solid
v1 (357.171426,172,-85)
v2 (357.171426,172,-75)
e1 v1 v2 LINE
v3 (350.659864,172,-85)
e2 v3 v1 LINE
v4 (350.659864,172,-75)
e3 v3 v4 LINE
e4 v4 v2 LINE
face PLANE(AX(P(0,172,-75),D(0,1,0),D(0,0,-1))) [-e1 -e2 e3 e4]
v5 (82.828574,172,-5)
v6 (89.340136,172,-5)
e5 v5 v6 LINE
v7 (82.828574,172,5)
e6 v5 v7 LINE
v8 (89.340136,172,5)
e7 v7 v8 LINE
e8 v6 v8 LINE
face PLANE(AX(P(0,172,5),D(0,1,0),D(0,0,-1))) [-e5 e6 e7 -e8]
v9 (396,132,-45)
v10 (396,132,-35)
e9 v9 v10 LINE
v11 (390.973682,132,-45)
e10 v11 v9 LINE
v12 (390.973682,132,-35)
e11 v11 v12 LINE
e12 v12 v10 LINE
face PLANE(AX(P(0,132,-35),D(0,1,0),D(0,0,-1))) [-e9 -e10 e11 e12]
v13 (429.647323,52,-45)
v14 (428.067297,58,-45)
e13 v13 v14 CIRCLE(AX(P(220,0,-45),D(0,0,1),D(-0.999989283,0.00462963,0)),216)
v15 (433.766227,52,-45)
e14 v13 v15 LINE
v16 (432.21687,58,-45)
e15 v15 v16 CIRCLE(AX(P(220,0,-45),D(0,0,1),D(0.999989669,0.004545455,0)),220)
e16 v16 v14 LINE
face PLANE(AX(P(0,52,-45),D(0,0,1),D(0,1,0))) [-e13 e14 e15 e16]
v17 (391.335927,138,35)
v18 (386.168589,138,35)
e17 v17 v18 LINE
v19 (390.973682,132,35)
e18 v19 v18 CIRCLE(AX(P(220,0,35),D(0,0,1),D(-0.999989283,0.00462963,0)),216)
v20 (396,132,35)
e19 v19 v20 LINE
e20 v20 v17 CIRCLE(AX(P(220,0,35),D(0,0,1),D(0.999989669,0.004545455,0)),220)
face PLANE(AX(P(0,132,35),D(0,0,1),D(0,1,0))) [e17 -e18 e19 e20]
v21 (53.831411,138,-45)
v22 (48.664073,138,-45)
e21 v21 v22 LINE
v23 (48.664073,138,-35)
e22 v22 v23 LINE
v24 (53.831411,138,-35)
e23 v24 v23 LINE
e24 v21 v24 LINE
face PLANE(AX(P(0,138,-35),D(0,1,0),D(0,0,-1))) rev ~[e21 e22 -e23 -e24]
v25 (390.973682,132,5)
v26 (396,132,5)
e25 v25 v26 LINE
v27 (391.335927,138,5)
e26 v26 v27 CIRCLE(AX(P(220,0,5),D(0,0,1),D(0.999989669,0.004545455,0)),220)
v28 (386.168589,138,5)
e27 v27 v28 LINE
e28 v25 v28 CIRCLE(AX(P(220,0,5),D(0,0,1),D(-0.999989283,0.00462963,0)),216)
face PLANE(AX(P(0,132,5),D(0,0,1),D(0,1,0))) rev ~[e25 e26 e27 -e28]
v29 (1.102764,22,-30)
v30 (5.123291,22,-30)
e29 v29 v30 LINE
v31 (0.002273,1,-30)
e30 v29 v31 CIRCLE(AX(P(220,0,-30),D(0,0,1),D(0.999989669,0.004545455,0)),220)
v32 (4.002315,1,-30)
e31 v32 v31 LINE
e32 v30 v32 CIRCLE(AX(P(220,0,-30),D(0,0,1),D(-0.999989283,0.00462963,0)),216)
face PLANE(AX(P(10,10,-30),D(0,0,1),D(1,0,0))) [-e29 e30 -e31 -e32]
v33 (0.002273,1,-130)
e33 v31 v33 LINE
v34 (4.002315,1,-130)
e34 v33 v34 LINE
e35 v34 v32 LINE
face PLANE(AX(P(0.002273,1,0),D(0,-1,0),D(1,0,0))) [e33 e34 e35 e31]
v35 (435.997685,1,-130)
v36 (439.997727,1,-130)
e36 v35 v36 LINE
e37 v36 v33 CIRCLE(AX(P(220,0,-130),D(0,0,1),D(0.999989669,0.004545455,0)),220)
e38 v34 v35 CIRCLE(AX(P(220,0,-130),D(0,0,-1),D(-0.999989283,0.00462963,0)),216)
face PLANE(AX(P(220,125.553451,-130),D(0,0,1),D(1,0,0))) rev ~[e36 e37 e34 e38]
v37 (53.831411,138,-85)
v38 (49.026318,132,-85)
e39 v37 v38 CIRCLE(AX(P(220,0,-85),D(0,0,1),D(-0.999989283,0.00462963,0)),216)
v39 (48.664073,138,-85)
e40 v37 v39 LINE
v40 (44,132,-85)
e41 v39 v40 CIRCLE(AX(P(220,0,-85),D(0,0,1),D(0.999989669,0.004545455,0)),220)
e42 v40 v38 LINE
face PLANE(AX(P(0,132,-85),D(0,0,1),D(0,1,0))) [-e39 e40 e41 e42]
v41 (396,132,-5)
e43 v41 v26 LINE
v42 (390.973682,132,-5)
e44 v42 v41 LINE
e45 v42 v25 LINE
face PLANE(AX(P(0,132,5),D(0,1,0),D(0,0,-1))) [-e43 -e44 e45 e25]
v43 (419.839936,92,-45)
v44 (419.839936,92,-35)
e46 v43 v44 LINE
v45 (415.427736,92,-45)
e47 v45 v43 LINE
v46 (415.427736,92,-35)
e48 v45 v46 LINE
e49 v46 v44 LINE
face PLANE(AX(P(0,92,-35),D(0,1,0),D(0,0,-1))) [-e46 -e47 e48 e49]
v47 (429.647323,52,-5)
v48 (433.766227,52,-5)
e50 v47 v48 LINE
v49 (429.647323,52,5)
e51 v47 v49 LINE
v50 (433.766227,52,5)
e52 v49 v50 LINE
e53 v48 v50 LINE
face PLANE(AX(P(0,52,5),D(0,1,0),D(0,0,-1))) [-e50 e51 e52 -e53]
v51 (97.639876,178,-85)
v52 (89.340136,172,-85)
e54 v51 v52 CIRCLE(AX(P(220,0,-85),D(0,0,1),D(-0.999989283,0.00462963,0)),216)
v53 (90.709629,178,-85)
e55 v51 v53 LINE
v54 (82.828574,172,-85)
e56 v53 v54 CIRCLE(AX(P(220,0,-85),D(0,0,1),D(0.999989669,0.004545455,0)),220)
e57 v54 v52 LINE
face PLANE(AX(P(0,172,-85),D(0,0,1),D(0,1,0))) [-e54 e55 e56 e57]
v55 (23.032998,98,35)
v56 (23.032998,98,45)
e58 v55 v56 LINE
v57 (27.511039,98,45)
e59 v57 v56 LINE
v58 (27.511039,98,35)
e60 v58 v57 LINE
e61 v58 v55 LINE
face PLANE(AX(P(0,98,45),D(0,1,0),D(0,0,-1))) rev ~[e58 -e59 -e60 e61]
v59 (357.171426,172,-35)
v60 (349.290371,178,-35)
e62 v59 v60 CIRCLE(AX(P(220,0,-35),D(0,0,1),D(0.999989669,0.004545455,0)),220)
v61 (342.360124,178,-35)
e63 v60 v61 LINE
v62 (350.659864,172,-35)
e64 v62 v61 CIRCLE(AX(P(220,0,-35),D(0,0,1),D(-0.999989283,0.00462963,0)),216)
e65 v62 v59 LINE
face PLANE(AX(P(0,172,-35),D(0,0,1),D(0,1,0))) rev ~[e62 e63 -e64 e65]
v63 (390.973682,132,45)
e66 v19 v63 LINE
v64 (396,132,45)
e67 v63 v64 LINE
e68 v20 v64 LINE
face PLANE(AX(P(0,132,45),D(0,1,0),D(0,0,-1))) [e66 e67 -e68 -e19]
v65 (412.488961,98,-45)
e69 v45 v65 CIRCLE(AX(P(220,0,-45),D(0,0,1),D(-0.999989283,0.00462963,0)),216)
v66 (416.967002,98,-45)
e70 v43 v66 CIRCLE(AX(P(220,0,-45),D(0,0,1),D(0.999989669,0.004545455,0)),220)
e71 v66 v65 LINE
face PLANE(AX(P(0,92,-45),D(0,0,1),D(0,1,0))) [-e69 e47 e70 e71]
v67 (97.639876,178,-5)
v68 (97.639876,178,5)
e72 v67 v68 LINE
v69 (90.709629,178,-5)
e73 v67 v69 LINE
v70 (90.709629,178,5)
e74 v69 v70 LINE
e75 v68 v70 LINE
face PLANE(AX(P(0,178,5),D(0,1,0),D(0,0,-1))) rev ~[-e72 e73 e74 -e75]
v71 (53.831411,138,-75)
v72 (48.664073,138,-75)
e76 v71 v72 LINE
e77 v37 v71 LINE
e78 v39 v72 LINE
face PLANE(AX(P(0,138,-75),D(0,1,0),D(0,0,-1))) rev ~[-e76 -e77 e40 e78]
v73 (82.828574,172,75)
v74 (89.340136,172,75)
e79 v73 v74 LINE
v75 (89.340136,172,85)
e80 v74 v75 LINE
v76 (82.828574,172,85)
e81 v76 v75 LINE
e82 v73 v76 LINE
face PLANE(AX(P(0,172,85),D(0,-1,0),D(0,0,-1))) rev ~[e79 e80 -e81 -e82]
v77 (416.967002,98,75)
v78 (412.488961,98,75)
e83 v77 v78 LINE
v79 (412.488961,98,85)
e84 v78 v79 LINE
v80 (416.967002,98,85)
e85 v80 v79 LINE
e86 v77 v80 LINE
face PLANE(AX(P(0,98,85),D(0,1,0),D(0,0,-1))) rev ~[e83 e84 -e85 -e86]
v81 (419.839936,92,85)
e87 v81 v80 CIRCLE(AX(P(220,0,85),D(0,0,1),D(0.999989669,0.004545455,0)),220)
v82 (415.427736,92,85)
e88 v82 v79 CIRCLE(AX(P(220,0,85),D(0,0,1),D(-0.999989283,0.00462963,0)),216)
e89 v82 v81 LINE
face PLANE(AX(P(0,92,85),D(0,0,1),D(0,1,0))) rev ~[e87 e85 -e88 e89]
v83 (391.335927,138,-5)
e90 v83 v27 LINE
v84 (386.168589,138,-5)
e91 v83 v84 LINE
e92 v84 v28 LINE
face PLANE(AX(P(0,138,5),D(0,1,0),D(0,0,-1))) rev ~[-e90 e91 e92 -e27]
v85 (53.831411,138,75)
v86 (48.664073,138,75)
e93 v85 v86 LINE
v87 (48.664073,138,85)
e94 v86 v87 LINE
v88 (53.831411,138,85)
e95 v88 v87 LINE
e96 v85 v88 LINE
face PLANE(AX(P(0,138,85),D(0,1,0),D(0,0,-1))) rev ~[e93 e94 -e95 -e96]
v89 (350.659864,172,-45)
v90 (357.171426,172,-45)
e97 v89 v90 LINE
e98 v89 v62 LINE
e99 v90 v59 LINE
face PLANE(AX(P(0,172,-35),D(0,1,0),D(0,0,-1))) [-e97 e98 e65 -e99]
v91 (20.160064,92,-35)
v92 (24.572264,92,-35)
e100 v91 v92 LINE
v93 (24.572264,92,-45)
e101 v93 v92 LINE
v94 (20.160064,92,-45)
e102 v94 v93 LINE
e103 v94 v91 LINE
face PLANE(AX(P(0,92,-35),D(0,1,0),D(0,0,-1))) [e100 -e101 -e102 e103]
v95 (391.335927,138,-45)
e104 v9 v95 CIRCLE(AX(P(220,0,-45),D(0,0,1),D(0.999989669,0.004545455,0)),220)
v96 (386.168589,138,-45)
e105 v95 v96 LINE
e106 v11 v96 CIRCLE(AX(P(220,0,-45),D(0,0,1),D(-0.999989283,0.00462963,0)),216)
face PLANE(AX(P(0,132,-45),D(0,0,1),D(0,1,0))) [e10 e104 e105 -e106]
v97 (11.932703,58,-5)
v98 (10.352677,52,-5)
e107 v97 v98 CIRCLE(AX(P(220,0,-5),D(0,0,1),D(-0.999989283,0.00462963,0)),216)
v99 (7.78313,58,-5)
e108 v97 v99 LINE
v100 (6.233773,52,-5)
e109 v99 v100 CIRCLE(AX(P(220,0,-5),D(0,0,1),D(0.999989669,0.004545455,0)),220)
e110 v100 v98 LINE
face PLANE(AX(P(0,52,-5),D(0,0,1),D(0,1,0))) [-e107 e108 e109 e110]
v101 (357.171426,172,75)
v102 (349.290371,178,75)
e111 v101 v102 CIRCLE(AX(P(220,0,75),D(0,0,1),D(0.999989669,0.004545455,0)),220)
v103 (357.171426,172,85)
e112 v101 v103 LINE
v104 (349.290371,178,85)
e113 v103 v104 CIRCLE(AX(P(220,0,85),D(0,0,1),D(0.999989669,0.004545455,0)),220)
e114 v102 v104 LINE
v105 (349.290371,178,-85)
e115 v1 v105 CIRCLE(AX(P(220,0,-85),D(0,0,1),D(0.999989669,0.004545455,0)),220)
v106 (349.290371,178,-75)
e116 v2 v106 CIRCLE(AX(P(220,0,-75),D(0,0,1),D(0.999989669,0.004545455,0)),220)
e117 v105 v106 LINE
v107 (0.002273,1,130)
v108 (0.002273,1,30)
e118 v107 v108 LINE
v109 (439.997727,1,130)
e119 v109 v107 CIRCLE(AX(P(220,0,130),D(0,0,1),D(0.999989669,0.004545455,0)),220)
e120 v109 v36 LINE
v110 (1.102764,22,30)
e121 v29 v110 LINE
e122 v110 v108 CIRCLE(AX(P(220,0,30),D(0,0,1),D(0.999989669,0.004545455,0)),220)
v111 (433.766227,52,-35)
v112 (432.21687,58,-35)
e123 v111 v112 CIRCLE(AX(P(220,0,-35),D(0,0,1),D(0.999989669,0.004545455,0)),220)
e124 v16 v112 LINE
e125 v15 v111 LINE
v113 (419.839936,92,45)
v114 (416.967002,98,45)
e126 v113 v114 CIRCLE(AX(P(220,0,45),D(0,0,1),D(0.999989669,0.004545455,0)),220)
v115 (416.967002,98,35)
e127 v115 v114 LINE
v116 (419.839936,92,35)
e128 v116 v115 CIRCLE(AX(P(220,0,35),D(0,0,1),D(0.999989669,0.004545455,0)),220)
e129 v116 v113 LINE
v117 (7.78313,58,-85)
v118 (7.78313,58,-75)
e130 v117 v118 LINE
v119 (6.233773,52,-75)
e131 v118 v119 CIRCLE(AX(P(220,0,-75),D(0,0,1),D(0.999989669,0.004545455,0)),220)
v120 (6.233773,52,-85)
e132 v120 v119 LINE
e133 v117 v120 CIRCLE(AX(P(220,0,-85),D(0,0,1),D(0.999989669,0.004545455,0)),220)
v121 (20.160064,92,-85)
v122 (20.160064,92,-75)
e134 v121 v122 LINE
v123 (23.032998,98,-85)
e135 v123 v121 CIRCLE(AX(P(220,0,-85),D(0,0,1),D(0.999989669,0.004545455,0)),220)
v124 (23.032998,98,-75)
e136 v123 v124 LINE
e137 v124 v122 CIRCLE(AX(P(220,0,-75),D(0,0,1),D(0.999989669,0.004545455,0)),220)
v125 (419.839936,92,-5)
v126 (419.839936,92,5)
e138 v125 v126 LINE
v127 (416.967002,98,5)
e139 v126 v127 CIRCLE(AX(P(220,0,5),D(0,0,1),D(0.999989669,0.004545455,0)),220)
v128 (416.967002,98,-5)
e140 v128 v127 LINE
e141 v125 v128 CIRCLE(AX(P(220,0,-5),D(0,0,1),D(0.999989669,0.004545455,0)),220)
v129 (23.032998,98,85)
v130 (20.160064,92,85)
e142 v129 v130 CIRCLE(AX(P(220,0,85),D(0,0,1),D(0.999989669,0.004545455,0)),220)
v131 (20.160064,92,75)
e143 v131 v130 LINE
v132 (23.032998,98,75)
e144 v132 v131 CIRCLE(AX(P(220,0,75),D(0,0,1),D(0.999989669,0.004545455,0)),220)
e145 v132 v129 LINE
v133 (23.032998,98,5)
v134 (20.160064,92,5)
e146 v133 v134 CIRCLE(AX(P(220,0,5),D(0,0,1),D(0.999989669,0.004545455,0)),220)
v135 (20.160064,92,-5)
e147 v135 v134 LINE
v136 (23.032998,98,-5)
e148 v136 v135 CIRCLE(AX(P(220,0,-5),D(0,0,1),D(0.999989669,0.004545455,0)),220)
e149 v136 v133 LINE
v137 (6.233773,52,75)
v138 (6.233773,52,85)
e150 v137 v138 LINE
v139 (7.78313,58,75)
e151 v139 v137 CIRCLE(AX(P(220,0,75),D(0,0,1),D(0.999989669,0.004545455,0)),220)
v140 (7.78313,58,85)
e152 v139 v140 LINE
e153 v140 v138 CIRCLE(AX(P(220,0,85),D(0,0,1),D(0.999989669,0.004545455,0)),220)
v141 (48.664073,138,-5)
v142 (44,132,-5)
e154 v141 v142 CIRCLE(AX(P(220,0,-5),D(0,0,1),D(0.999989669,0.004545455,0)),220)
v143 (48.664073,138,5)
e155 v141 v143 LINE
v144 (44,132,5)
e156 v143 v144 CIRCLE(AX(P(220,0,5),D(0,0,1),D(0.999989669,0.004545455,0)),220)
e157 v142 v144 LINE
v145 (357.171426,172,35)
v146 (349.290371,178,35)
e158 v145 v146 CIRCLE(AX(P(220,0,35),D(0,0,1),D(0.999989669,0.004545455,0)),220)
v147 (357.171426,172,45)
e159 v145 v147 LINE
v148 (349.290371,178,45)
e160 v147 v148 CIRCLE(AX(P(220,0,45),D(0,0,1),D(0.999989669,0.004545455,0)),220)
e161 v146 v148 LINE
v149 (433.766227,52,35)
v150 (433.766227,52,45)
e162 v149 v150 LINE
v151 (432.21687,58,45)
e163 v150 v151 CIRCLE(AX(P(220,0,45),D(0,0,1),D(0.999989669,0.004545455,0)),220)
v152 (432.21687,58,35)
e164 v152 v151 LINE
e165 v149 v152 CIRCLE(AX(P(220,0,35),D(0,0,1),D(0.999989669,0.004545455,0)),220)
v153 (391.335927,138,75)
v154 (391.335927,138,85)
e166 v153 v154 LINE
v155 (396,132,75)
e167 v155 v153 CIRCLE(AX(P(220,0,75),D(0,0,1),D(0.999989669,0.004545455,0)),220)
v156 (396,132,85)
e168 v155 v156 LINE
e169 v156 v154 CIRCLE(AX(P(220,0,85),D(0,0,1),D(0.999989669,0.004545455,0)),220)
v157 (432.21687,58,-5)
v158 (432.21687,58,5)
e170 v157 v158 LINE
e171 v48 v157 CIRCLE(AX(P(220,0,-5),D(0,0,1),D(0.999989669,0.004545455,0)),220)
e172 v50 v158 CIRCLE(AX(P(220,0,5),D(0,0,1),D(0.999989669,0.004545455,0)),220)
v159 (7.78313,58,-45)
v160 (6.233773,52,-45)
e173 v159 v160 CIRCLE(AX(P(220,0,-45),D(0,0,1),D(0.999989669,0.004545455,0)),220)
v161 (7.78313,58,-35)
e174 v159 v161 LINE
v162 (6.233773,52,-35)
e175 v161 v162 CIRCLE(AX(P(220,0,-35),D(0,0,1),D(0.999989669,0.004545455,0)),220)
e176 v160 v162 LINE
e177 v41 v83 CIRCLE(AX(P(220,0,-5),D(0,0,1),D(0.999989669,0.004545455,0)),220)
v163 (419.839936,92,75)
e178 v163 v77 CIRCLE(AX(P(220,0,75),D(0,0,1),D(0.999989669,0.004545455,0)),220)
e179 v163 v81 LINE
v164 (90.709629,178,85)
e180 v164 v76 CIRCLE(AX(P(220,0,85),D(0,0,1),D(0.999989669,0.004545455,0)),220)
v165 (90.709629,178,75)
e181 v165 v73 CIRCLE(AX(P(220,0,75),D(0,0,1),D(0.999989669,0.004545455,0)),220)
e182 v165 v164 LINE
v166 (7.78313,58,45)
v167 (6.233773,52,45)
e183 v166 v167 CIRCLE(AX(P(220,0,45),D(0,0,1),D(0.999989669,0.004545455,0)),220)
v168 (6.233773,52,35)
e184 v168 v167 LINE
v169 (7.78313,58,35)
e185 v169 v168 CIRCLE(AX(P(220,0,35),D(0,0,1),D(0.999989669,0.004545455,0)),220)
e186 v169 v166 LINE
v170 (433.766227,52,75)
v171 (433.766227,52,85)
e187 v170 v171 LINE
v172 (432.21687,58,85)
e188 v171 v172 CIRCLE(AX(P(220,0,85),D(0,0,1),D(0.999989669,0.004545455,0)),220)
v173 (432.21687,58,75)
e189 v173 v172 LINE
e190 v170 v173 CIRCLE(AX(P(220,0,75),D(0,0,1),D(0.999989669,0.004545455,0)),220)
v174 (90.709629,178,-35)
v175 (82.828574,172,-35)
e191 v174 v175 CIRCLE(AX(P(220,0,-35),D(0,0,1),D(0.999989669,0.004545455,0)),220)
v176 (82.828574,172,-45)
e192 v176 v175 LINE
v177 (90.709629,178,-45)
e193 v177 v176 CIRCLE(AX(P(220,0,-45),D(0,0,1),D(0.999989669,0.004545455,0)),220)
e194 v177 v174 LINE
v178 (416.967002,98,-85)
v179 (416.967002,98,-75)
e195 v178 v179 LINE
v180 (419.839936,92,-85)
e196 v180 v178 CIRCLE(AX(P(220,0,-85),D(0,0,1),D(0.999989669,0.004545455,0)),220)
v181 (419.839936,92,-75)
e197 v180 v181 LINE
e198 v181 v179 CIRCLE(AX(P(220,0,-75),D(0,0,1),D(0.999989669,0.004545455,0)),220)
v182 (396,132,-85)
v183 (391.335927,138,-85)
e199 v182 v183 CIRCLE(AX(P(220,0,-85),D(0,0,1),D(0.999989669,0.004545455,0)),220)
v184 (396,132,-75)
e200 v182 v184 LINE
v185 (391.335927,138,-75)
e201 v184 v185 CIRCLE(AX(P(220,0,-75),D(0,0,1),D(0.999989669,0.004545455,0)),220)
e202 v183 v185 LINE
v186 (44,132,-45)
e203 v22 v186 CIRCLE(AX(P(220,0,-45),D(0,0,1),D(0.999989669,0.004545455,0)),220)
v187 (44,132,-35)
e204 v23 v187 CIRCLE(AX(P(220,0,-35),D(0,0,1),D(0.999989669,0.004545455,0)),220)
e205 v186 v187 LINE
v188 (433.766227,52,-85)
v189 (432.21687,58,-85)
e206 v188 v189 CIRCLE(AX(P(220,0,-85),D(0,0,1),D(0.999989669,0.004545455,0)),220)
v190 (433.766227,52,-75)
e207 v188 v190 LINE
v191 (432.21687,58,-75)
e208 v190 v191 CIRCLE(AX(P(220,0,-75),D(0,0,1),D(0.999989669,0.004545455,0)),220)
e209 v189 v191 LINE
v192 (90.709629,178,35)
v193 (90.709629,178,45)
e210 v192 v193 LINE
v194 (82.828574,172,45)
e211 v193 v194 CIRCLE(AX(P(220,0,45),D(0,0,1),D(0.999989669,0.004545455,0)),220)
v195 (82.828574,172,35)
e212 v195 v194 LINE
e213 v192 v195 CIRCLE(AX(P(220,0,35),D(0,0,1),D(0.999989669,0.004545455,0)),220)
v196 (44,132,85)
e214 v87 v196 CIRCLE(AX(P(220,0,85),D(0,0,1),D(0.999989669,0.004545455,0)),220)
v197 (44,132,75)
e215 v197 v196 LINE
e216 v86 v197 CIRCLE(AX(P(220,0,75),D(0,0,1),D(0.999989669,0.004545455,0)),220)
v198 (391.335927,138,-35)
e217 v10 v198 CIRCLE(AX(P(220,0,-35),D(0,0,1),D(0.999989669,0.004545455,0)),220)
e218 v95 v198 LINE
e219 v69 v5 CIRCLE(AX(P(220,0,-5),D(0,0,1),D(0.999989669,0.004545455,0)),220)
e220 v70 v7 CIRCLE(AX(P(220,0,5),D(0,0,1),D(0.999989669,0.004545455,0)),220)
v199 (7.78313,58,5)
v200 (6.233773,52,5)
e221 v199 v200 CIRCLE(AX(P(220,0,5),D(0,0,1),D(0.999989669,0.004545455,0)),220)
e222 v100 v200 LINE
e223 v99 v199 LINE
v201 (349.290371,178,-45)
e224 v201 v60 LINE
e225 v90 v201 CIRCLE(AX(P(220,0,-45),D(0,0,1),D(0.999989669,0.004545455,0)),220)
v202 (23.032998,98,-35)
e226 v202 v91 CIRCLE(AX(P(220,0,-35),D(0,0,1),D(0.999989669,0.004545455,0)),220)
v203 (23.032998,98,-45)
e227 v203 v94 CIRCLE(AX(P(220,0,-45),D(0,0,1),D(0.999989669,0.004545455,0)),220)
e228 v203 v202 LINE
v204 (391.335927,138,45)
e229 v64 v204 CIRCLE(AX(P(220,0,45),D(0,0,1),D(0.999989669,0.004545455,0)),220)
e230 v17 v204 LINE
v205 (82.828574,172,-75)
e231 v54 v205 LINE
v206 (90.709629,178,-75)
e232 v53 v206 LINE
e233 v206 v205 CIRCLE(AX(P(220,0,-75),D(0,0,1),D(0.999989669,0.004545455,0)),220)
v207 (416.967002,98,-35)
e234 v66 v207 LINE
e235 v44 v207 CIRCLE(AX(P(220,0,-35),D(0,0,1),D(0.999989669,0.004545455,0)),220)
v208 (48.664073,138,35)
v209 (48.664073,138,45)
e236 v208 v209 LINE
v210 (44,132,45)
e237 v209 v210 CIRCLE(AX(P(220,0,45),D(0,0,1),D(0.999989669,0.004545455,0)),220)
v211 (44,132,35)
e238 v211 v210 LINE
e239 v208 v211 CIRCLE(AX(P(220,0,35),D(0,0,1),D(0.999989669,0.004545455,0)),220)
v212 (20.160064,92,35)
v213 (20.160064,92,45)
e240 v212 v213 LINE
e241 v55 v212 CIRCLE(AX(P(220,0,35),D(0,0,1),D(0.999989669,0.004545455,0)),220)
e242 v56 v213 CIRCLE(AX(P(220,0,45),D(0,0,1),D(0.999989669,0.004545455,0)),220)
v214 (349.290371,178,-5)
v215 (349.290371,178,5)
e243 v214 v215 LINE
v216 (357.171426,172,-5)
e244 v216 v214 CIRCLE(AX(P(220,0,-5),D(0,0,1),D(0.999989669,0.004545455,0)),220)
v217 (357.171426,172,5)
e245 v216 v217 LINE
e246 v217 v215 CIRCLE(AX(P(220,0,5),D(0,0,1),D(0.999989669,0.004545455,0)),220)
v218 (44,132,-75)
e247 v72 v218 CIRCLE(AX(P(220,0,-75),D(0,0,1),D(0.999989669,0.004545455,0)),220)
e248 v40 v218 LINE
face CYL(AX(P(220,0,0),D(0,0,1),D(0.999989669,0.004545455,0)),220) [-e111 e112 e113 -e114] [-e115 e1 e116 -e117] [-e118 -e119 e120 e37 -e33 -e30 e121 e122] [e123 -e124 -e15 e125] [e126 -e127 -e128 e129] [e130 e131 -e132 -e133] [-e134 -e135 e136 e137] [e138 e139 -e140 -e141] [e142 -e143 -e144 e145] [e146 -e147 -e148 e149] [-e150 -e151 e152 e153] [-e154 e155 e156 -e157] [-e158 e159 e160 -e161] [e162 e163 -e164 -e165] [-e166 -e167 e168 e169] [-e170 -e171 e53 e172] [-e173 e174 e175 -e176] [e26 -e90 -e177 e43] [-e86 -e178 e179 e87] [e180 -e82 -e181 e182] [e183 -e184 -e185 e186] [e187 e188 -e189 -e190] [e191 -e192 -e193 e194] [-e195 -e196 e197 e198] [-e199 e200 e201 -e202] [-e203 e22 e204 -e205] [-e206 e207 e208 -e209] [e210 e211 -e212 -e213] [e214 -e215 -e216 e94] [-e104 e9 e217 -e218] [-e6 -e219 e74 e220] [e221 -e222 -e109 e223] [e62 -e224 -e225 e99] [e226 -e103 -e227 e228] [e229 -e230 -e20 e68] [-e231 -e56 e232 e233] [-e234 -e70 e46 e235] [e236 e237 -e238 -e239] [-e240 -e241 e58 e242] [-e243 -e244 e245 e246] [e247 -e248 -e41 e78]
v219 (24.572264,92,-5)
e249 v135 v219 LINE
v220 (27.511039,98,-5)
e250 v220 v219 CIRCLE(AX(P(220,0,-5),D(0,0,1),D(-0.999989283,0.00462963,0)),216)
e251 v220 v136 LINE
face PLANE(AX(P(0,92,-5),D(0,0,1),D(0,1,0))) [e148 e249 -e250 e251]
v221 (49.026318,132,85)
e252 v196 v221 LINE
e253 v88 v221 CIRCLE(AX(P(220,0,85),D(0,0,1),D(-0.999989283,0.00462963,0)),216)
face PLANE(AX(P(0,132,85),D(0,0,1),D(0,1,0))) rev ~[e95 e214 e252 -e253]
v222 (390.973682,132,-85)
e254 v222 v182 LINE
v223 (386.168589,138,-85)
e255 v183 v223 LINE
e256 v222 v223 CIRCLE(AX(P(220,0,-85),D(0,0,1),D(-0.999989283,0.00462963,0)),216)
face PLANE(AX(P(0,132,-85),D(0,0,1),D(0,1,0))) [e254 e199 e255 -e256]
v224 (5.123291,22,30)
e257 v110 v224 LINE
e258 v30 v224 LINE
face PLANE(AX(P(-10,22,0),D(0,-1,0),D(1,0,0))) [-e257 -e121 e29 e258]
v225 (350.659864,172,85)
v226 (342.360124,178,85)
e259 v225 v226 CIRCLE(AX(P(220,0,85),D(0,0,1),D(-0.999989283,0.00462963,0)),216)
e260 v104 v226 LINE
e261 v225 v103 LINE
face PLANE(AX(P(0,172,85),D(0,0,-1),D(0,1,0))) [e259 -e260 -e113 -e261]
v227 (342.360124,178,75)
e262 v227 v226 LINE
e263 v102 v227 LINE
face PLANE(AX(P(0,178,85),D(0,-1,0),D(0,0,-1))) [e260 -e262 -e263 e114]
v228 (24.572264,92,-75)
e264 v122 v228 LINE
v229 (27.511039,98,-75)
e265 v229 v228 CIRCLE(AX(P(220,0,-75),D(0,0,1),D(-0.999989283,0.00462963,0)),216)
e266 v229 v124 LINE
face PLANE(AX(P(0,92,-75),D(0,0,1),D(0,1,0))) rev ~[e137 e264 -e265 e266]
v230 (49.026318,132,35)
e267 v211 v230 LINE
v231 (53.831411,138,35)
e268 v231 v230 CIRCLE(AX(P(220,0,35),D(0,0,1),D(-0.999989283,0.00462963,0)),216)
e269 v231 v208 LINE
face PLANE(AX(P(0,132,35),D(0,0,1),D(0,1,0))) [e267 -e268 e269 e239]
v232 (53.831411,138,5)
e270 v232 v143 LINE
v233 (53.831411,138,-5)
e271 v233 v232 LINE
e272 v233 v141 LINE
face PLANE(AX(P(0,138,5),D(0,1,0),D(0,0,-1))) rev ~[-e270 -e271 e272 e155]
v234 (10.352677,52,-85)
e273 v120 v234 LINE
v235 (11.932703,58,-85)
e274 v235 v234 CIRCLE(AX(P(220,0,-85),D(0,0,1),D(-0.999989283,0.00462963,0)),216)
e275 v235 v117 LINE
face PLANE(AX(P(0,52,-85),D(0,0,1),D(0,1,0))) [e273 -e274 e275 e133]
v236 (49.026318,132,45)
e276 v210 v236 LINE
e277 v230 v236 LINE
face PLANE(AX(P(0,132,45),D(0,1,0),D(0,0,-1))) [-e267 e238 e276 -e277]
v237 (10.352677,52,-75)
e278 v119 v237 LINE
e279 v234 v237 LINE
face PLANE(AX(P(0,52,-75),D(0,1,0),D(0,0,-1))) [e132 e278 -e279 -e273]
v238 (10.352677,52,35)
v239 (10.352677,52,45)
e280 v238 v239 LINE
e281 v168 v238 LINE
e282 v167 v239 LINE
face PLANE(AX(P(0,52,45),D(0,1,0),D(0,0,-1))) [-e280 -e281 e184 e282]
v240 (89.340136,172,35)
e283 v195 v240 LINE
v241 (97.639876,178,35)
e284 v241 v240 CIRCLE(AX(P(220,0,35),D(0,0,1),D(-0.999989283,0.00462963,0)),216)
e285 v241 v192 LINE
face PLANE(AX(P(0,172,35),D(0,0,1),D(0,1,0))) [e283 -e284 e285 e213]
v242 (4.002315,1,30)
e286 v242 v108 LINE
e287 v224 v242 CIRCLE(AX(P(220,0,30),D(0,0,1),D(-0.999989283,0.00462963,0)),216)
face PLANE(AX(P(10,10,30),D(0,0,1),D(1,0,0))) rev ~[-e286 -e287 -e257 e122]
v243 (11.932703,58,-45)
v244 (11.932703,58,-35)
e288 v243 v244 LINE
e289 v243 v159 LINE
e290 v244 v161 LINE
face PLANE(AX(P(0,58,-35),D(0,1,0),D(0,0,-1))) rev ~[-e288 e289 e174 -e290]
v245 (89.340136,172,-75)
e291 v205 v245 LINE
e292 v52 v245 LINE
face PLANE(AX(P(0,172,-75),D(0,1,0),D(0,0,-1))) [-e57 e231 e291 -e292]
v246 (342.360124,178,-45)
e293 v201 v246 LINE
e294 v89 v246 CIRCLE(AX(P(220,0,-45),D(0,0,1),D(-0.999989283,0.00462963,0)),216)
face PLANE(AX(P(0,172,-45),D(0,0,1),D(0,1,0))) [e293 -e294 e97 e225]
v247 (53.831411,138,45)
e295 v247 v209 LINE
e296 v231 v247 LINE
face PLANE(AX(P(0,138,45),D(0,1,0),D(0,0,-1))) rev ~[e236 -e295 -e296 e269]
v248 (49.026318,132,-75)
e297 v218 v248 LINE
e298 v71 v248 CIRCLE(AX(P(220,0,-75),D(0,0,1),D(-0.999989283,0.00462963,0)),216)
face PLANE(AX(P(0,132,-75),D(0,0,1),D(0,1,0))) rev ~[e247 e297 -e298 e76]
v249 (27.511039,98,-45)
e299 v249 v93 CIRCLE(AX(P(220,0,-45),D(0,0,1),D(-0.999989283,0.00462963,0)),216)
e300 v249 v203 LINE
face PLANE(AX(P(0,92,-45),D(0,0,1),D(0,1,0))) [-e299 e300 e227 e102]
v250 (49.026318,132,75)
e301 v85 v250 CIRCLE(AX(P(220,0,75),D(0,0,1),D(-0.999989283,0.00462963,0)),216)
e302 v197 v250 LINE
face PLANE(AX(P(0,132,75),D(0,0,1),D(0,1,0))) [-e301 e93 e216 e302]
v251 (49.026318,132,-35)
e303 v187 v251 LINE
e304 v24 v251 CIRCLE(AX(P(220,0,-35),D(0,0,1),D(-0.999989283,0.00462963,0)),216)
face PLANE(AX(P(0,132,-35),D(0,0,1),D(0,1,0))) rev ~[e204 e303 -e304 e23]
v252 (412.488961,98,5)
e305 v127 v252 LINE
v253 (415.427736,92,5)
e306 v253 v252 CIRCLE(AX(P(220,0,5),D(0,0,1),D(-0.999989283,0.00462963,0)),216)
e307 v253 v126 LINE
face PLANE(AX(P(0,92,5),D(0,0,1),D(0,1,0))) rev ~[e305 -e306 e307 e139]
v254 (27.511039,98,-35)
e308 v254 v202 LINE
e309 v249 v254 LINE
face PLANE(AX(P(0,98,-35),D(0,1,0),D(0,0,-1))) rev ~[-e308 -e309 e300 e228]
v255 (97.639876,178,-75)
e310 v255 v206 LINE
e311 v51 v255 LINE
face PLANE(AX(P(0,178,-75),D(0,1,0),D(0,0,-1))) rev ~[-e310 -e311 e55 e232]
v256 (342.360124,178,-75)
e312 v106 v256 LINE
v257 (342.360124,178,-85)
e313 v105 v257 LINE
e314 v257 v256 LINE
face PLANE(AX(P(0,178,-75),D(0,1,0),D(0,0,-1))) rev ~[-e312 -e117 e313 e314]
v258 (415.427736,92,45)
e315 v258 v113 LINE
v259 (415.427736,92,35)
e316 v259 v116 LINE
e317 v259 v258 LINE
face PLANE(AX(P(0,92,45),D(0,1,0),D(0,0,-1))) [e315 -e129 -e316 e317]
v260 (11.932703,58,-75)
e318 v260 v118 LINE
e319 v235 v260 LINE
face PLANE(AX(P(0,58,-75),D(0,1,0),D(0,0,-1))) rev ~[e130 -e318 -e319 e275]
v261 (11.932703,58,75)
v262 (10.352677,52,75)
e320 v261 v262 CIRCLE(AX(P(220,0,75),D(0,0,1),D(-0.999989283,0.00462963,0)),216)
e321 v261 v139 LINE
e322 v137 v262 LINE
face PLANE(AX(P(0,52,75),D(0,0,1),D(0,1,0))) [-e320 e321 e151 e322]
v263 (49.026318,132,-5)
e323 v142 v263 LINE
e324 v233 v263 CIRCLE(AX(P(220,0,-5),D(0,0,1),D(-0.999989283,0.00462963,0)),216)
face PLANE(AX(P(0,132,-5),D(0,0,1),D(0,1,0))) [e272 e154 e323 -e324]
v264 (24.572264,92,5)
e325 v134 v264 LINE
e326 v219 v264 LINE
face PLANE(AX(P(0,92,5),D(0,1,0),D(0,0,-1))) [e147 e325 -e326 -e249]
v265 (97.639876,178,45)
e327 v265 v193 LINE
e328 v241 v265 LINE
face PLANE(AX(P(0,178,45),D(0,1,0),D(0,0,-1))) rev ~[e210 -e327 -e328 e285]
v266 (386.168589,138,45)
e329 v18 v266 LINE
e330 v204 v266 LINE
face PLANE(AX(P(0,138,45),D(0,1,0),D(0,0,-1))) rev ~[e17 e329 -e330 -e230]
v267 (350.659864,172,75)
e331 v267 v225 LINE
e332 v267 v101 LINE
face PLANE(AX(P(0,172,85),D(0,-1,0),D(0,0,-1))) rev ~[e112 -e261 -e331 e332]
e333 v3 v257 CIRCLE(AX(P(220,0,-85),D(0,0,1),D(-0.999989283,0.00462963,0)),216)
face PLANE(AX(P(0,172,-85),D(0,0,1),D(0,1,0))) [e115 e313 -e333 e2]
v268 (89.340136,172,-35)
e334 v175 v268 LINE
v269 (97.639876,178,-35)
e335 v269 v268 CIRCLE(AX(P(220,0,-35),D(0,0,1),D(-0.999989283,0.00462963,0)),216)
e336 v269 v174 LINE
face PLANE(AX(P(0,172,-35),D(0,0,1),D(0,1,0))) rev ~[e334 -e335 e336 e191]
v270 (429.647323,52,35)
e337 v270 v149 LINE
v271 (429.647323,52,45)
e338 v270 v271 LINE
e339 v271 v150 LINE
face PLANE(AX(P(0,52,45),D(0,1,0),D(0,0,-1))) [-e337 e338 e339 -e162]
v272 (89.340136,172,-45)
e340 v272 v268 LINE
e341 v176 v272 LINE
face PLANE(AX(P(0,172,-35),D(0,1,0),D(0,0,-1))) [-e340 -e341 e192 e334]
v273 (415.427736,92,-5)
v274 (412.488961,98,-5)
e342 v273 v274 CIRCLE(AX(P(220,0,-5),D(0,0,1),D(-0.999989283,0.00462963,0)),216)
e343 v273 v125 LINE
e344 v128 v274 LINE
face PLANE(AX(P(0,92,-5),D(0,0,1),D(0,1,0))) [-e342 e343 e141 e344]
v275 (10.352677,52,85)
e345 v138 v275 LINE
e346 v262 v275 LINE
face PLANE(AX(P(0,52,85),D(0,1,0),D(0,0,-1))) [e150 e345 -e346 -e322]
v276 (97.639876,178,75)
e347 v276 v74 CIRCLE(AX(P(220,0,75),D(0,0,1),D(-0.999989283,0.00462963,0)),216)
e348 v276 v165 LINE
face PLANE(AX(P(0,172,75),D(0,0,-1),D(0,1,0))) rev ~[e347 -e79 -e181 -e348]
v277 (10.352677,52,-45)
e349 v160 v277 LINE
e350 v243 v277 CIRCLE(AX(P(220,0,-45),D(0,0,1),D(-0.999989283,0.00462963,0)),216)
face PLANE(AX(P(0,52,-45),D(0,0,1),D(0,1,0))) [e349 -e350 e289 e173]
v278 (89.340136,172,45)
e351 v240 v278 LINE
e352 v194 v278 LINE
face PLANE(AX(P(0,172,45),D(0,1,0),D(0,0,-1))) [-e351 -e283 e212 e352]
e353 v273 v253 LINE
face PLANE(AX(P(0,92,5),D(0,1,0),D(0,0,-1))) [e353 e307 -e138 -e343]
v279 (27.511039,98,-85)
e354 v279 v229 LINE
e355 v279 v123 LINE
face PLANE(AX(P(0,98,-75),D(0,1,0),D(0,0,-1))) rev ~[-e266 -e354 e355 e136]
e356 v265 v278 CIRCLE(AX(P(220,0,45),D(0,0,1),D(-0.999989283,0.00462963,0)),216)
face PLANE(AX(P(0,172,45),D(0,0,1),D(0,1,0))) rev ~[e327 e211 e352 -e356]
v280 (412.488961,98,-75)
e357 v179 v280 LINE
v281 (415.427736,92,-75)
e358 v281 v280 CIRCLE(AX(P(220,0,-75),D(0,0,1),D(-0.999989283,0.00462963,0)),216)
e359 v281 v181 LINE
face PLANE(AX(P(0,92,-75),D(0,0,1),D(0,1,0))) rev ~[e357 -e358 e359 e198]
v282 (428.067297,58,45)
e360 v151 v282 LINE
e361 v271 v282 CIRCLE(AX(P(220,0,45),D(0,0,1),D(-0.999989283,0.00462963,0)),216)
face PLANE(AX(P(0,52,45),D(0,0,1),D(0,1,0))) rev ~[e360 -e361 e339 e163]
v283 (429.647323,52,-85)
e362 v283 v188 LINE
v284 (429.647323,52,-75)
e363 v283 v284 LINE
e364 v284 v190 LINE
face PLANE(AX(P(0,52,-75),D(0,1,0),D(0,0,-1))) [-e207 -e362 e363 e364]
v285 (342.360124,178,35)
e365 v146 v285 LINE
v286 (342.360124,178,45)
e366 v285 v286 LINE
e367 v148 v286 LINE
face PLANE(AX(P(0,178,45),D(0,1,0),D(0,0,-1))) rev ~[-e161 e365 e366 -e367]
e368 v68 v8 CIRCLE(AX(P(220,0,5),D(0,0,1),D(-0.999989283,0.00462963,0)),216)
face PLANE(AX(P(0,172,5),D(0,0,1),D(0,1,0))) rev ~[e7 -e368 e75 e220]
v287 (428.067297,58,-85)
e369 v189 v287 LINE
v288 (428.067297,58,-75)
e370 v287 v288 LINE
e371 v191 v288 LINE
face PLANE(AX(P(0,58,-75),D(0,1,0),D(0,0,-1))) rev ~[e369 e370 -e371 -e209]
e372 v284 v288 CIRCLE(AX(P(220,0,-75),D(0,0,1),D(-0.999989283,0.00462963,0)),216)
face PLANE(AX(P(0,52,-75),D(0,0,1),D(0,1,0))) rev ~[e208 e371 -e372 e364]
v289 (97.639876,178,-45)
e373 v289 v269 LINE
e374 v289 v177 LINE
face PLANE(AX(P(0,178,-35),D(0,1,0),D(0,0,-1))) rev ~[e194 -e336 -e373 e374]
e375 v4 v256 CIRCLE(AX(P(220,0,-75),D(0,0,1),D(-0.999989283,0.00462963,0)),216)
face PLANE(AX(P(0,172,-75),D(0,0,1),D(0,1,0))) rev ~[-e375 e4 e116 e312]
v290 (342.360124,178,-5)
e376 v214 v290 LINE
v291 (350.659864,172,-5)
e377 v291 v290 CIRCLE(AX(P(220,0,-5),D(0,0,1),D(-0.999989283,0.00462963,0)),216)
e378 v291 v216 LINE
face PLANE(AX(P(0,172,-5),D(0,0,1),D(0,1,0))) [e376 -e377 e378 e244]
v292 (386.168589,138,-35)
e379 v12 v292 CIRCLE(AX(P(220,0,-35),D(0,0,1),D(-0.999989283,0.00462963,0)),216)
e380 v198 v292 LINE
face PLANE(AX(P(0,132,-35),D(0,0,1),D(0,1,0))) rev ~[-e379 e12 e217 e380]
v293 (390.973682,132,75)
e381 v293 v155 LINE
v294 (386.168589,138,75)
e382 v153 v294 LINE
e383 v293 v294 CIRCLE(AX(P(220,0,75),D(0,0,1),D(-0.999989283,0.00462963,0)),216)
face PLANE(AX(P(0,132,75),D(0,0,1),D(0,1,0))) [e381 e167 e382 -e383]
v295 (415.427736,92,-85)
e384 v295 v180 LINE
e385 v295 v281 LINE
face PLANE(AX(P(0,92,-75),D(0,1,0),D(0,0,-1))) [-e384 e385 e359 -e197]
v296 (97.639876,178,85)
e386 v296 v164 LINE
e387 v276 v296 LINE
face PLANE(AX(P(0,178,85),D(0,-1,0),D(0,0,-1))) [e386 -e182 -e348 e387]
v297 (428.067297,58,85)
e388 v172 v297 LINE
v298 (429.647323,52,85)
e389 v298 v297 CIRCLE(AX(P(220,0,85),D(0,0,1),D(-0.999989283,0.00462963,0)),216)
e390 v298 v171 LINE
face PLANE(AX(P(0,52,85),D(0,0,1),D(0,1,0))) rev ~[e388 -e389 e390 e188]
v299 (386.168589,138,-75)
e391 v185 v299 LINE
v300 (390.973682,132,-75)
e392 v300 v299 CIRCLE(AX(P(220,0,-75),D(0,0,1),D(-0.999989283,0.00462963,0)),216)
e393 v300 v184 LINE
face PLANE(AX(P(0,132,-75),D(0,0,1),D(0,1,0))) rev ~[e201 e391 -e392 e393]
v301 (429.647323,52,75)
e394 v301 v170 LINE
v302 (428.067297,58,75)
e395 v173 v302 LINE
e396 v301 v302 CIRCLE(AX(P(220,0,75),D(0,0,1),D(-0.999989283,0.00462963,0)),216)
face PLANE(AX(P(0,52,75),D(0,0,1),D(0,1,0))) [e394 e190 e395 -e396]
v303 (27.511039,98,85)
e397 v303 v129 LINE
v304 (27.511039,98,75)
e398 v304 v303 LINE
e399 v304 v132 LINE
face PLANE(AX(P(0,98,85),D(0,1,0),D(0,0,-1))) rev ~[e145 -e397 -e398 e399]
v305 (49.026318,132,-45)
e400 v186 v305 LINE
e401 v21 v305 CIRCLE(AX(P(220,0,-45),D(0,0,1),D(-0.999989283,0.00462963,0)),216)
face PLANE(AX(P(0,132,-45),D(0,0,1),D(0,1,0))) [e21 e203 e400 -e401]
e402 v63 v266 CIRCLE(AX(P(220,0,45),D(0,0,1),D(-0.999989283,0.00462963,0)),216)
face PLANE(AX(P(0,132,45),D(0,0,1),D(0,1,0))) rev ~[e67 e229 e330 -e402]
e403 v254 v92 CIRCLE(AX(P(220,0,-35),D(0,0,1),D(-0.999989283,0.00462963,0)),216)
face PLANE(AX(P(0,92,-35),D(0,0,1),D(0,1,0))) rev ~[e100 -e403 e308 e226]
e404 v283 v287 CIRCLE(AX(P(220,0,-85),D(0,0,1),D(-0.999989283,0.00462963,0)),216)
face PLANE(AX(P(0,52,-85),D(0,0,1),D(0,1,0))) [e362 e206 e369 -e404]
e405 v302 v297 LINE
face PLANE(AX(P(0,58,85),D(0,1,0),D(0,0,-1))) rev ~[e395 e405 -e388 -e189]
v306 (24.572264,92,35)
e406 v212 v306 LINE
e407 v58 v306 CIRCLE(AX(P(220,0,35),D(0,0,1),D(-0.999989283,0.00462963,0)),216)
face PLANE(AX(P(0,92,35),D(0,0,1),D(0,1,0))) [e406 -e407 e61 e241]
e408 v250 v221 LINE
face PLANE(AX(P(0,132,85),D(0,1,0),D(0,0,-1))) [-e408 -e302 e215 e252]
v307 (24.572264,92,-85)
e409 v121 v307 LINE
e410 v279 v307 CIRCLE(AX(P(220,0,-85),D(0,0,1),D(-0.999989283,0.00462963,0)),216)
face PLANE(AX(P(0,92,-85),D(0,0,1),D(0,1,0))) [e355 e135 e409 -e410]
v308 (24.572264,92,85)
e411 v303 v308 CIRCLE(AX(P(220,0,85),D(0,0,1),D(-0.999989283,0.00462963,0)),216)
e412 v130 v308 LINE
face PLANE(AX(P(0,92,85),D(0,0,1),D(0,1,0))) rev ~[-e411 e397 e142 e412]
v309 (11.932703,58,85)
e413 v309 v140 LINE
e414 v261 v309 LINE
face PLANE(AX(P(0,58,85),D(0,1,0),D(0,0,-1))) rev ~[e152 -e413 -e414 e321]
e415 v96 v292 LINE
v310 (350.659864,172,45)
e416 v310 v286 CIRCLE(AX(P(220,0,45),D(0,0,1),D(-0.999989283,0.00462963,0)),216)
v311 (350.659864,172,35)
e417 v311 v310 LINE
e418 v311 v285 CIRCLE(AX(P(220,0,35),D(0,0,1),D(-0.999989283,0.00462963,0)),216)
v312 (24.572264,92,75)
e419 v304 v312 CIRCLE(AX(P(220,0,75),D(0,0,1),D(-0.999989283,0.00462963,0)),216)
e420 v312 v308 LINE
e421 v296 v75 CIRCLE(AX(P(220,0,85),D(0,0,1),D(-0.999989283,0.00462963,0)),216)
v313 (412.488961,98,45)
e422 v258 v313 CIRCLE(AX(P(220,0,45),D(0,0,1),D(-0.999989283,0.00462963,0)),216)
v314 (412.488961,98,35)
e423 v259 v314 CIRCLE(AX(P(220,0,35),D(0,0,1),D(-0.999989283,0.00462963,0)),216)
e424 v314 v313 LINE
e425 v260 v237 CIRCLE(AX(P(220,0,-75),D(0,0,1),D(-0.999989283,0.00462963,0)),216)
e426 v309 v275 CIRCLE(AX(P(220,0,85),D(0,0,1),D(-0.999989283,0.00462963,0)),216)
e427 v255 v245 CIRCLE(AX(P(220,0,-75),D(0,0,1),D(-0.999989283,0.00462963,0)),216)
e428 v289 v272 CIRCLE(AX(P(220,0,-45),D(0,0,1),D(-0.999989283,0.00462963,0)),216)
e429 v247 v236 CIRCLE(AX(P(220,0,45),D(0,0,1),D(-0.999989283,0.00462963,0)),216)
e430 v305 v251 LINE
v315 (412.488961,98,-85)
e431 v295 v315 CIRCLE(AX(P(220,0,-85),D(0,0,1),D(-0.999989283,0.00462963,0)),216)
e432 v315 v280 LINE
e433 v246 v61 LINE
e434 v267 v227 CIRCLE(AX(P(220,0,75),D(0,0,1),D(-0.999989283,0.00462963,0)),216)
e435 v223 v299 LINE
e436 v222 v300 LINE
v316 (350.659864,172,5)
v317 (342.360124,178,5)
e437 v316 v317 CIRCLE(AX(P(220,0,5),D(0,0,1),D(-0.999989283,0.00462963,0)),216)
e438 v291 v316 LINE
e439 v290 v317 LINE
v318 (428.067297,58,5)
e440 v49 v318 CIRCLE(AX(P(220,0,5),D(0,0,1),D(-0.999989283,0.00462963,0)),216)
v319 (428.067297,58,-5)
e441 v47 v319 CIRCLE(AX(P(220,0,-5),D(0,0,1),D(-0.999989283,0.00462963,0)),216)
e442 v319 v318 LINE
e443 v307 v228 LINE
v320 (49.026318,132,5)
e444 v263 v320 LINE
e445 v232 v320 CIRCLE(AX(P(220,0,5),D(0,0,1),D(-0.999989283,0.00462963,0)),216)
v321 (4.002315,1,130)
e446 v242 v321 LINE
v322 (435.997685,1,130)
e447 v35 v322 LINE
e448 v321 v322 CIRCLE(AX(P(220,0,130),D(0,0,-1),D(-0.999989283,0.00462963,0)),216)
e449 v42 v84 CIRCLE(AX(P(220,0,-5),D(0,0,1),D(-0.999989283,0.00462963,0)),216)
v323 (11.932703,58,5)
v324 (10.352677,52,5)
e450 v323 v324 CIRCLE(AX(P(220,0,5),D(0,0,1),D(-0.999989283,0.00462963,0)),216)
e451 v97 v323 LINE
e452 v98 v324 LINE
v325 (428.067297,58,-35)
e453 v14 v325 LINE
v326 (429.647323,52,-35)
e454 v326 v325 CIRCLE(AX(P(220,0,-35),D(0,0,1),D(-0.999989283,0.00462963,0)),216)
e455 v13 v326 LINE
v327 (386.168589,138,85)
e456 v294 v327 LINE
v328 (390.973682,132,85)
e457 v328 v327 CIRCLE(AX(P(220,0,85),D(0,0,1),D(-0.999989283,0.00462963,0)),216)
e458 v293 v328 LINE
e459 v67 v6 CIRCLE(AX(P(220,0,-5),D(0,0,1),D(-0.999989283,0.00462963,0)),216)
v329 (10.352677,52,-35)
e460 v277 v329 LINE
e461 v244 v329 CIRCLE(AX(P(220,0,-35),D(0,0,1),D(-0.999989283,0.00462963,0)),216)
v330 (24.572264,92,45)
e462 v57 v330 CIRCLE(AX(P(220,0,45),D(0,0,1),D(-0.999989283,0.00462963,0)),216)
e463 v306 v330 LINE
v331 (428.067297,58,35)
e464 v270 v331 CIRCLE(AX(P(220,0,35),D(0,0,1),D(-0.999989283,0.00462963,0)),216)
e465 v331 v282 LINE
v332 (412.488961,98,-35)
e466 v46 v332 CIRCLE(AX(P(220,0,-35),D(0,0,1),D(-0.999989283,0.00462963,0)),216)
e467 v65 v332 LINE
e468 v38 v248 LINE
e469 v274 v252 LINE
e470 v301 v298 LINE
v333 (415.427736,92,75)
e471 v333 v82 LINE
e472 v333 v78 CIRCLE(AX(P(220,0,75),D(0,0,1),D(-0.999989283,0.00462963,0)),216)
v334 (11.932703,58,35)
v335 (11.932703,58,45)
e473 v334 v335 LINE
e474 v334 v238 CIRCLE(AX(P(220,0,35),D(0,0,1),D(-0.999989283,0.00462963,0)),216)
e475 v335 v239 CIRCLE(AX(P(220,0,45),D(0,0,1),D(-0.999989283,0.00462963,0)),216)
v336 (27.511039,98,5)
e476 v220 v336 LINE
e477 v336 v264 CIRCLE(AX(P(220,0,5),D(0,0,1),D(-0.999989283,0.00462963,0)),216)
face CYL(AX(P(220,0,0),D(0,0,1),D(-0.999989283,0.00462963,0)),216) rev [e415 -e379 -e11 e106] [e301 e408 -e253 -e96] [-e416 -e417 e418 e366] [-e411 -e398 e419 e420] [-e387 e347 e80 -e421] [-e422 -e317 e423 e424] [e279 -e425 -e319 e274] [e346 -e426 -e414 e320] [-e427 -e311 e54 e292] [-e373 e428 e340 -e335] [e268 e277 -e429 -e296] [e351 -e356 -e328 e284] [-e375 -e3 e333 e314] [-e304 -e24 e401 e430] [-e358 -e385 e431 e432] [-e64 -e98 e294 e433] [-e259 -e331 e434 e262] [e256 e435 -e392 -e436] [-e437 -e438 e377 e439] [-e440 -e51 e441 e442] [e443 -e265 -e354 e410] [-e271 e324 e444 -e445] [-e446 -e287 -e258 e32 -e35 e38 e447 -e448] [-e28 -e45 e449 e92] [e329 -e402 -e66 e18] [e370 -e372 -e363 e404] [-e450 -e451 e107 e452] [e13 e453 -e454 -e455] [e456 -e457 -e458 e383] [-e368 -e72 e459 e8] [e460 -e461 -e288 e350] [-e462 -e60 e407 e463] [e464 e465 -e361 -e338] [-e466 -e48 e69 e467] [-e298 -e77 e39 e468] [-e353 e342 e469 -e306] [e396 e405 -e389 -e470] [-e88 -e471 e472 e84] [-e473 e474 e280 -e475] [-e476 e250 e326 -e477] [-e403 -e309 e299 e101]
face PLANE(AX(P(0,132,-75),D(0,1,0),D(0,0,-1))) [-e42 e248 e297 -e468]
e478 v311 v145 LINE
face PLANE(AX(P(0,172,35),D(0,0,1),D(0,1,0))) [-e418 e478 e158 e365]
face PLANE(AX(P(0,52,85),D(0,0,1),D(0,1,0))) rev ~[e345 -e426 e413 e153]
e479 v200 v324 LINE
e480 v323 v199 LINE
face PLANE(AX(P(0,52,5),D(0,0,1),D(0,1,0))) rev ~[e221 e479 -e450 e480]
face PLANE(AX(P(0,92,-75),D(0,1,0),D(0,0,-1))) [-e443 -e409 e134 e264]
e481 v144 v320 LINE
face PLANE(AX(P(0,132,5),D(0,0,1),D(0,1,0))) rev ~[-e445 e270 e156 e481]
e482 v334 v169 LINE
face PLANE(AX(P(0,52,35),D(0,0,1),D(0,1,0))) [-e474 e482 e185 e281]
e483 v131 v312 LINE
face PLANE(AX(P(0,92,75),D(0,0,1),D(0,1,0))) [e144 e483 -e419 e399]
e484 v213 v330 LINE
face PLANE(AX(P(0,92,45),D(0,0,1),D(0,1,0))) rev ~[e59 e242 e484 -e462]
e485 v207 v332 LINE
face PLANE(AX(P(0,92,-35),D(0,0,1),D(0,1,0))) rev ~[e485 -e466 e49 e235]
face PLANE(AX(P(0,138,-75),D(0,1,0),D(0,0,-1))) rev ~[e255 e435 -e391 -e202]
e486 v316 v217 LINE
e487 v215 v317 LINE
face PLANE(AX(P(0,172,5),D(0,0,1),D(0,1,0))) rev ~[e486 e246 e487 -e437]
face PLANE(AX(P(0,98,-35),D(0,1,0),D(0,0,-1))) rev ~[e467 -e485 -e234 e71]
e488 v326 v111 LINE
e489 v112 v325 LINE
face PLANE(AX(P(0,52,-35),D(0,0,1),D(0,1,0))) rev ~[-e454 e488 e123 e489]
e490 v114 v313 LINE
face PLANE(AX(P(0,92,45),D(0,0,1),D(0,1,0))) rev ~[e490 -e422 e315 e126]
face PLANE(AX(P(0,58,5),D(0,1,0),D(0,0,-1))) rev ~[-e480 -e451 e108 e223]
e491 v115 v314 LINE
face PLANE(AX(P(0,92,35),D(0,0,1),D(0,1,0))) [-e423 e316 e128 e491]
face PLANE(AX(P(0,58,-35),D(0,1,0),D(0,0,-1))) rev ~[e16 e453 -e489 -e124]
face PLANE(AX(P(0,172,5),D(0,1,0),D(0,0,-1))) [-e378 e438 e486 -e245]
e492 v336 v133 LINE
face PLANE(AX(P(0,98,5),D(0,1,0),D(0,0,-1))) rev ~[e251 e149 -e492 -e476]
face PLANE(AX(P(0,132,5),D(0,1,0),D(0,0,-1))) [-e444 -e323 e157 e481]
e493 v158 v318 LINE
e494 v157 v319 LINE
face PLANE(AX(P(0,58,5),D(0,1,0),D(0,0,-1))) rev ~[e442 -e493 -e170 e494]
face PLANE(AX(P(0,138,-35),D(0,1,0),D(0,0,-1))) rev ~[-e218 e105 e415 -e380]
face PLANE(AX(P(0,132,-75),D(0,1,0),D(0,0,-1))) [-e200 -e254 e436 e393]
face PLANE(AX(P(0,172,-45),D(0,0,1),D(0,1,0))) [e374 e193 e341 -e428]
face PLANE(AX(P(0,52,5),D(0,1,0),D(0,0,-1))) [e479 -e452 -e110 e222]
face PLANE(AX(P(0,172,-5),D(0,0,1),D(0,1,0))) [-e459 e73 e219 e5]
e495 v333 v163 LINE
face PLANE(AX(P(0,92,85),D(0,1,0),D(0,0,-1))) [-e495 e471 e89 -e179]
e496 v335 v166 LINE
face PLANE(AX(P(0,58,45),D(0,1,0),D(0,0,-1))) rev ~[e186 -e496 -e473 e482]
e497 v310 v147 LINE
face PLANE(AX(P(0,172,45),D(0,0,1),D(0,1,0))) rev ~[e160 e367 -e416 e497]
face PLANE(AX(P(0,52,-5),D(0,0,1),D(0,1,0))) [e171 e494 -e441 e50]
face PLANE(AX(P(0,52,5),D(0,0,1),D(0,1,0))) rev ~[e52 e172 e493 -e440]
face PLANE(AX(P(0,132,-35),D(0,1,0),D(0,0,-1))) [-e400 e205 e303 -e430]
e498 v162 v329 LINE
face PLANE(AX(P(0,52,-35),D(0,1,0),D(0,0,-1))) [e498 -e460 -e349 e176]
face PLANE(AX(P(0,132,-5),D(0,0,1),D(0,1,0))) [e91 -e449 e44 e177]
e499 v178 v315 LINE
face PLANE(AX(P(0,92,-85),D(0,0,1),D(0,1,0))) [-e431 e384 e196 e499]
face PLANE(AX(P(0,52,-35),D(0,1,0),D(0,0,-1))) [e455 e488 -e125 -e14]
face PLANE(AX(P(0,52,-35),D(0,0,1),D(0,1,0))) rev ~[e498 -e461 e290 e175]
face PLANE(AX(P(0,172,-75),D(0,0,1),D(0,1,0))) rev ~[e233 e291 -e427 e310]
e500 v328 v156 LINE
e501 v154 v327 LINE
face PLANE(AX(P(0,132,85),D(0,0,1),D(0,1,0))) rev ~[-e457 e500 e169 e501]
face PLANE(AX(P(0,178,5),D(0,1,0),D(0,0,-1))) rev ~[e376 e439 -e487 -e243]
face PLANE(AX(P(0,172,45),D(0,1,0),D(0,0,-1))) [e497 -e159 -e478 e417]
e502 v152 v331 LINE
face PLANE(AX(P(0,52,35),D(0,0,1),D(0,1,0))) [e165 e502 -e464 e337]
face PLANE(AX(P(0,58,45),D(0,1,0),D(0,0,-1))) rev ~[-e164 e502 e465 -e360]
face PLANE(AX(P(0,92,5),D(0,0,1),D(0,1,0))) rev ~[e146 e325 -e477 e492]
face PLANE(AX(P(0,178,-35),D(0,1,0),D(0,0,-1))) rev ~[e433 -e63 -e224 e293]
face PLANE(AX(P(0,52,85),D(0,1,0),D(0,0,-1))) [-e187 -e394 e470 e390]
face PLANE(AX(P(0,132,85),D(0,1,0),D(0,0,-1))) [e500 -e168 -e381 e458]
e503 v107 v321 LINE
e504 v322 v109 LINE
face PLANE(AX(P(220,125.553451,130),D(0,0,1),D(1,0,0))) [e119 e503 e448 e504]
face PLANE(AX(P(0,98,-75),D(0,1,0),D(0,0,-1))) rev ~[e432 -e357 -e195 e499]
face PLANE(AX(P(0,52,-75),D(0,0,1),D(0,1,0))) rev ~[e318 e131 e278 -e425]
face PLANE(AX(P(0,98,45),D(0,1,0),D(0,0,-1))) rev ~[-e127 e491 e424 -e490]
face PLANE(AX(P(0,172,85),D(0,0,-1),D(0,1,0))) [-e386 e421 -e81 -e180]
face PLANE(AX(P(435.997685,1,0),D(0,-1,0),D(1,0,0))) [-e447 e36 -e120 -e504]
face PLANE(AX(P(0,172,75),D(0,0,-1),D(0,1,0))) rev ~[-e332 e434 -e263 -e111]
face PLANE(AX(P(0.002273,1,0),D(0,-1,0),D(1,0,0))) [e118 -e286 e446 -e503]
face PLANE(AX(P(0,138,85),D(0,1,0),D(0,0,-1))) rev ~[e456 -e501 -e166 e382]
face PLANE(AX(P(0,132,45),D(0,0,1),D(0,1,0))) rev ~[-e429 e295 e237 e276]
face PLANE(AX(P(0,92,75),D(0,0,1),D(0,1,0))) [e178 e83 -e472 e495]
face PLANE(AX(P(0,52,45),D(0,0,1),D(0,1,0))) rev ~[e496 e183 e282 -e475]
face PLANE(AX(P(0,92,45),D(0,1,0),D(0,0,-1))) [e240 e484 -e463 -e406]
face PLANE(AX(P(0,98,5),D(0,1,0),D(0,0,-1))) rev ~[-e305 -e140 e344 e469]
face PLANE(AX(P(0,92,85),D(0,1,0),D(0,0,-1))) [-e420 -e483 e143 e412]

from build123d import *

# Parameters (mm, degrees)
EXTRUDE_1_DEPTH     = 130
SKETCH_2_W          = 10
SKETCH_2_H          = 6
CUT_EXTRUDE_1_DEPTH = 500
SKETCH_3_W          = 40
SKETCH_3_H          = 24
CUT_EXTRUDE_2_DEPTH = 30


with BuildPart() as part:
    # 草图1 → 凸台-拉伸1 (new, symmetric)
    with BuildSketch(Plane.XY):
        with BuildLine():
            Line((0.002272739, 1), (4.002314827, 1))
            ThreePointArc((4.002314827, 1), (220, 216), (435.997685173, 1))
            Line((435.997685173, 1), (439.997727261, 1))
            ThreePointArc((439.997727261, 1), (220, 220), (0.002272739, 1))
        make_face()
    extrude(amount=EXTRUDE_1_DEPTH, both=True)

    # 草图2 → 切除-拉伸1 (cut, symmetric)
    with BuildSketch(Plane(origin=(0, 0, 0), x_dir=(0, 0, -1), z_dir=(1, 0, 0))):
        with Locations((80, 55)):
            Rectangle(SKETCH_2_W, SKETCH_2_H)
        with Locations((40, 55)):
            Rectangle(SKETCH_2_W, SKETCH_2_H)
        with Locations((0, 55)):
            Rectangle(SKETCH_2_W, SKETCH_2_H)
        with Locations((-40, 55)):
            Rectangle(SKETCH_2_W, SKETCH_2_H)
        with Locations((-80, 55)):
            Rectangle(SKETCH_2_W, SKETCH_2_H)
        with Locations((80, 95)):
            Rectangle(SKETCH_2_W, SKETCH_2_H)
        with Locations((40, 95)):
            Rectangle(SKETCH_2_W, SKETCH_2_H)
        with Locations((0, 95)):
            Rectangle(SKETCH_2_W, SKETCH_2_H)
        with Locations((-40, 95)):
            Rectangle(SKETCH_2_W, SKETCH_2_H)
        with Locations((-80, 95)):
            Rectangle(SKETCH_2_W, SKETCH_2_H)
        with Locations((80, 135)):
            Rectangle(SKETCH_2_W, SKETCH_2_H)
        with Locations((40, 135)):
            Rectangle(SKETCH_2_W, SKETCH_2_H)
        with Locations((0, 135)):
            Rectangle(SKETCH_2_W, SKETCH_2_H)
        with Locations((-40, 135)):
            Rectangle(SKETCH_2_W, SKETCH_2_H)
        with Locations((-80, 135)):
            Rectangle(SKETCH_2_W, SKETCH_2_H)
        with Locations((80, 175)):
            Rectangle(SKETCH_2_W, SKETCH_2_H)
        with Locations((40, 175)):
            Rectangle(SKETCH_2_W, SKETCH_2_H)
        with Locations((0, 175)):
            Rectangle(SKETCH_2_W, SKETCH_2_H)
        with Locations((-40, 175)):
            Rectangle(SKETCH_2_W, SKETCH_2_H)
        with Locations((-80, 175)):
            Rectangle(SKETCH_2_W, SKETCH_2_H)
    extrude(amount=CUT_EXTRUDE_1_DEPTH, both=True, mode=Mode.SUBTRACT)

    # 草图3 → 切除-拉伸2 (cut, symmetric)
    with BuildSketch(Plane.XY):
        with Locations((10, 10)):
            Rectangle(SKETCH_3_W, SKETCH_3_H)
    extrude(amount=CUT_EXTRUDE_2_DEPTH, both=True, mode=Mode.SUBTRACT)


solid = part.part
